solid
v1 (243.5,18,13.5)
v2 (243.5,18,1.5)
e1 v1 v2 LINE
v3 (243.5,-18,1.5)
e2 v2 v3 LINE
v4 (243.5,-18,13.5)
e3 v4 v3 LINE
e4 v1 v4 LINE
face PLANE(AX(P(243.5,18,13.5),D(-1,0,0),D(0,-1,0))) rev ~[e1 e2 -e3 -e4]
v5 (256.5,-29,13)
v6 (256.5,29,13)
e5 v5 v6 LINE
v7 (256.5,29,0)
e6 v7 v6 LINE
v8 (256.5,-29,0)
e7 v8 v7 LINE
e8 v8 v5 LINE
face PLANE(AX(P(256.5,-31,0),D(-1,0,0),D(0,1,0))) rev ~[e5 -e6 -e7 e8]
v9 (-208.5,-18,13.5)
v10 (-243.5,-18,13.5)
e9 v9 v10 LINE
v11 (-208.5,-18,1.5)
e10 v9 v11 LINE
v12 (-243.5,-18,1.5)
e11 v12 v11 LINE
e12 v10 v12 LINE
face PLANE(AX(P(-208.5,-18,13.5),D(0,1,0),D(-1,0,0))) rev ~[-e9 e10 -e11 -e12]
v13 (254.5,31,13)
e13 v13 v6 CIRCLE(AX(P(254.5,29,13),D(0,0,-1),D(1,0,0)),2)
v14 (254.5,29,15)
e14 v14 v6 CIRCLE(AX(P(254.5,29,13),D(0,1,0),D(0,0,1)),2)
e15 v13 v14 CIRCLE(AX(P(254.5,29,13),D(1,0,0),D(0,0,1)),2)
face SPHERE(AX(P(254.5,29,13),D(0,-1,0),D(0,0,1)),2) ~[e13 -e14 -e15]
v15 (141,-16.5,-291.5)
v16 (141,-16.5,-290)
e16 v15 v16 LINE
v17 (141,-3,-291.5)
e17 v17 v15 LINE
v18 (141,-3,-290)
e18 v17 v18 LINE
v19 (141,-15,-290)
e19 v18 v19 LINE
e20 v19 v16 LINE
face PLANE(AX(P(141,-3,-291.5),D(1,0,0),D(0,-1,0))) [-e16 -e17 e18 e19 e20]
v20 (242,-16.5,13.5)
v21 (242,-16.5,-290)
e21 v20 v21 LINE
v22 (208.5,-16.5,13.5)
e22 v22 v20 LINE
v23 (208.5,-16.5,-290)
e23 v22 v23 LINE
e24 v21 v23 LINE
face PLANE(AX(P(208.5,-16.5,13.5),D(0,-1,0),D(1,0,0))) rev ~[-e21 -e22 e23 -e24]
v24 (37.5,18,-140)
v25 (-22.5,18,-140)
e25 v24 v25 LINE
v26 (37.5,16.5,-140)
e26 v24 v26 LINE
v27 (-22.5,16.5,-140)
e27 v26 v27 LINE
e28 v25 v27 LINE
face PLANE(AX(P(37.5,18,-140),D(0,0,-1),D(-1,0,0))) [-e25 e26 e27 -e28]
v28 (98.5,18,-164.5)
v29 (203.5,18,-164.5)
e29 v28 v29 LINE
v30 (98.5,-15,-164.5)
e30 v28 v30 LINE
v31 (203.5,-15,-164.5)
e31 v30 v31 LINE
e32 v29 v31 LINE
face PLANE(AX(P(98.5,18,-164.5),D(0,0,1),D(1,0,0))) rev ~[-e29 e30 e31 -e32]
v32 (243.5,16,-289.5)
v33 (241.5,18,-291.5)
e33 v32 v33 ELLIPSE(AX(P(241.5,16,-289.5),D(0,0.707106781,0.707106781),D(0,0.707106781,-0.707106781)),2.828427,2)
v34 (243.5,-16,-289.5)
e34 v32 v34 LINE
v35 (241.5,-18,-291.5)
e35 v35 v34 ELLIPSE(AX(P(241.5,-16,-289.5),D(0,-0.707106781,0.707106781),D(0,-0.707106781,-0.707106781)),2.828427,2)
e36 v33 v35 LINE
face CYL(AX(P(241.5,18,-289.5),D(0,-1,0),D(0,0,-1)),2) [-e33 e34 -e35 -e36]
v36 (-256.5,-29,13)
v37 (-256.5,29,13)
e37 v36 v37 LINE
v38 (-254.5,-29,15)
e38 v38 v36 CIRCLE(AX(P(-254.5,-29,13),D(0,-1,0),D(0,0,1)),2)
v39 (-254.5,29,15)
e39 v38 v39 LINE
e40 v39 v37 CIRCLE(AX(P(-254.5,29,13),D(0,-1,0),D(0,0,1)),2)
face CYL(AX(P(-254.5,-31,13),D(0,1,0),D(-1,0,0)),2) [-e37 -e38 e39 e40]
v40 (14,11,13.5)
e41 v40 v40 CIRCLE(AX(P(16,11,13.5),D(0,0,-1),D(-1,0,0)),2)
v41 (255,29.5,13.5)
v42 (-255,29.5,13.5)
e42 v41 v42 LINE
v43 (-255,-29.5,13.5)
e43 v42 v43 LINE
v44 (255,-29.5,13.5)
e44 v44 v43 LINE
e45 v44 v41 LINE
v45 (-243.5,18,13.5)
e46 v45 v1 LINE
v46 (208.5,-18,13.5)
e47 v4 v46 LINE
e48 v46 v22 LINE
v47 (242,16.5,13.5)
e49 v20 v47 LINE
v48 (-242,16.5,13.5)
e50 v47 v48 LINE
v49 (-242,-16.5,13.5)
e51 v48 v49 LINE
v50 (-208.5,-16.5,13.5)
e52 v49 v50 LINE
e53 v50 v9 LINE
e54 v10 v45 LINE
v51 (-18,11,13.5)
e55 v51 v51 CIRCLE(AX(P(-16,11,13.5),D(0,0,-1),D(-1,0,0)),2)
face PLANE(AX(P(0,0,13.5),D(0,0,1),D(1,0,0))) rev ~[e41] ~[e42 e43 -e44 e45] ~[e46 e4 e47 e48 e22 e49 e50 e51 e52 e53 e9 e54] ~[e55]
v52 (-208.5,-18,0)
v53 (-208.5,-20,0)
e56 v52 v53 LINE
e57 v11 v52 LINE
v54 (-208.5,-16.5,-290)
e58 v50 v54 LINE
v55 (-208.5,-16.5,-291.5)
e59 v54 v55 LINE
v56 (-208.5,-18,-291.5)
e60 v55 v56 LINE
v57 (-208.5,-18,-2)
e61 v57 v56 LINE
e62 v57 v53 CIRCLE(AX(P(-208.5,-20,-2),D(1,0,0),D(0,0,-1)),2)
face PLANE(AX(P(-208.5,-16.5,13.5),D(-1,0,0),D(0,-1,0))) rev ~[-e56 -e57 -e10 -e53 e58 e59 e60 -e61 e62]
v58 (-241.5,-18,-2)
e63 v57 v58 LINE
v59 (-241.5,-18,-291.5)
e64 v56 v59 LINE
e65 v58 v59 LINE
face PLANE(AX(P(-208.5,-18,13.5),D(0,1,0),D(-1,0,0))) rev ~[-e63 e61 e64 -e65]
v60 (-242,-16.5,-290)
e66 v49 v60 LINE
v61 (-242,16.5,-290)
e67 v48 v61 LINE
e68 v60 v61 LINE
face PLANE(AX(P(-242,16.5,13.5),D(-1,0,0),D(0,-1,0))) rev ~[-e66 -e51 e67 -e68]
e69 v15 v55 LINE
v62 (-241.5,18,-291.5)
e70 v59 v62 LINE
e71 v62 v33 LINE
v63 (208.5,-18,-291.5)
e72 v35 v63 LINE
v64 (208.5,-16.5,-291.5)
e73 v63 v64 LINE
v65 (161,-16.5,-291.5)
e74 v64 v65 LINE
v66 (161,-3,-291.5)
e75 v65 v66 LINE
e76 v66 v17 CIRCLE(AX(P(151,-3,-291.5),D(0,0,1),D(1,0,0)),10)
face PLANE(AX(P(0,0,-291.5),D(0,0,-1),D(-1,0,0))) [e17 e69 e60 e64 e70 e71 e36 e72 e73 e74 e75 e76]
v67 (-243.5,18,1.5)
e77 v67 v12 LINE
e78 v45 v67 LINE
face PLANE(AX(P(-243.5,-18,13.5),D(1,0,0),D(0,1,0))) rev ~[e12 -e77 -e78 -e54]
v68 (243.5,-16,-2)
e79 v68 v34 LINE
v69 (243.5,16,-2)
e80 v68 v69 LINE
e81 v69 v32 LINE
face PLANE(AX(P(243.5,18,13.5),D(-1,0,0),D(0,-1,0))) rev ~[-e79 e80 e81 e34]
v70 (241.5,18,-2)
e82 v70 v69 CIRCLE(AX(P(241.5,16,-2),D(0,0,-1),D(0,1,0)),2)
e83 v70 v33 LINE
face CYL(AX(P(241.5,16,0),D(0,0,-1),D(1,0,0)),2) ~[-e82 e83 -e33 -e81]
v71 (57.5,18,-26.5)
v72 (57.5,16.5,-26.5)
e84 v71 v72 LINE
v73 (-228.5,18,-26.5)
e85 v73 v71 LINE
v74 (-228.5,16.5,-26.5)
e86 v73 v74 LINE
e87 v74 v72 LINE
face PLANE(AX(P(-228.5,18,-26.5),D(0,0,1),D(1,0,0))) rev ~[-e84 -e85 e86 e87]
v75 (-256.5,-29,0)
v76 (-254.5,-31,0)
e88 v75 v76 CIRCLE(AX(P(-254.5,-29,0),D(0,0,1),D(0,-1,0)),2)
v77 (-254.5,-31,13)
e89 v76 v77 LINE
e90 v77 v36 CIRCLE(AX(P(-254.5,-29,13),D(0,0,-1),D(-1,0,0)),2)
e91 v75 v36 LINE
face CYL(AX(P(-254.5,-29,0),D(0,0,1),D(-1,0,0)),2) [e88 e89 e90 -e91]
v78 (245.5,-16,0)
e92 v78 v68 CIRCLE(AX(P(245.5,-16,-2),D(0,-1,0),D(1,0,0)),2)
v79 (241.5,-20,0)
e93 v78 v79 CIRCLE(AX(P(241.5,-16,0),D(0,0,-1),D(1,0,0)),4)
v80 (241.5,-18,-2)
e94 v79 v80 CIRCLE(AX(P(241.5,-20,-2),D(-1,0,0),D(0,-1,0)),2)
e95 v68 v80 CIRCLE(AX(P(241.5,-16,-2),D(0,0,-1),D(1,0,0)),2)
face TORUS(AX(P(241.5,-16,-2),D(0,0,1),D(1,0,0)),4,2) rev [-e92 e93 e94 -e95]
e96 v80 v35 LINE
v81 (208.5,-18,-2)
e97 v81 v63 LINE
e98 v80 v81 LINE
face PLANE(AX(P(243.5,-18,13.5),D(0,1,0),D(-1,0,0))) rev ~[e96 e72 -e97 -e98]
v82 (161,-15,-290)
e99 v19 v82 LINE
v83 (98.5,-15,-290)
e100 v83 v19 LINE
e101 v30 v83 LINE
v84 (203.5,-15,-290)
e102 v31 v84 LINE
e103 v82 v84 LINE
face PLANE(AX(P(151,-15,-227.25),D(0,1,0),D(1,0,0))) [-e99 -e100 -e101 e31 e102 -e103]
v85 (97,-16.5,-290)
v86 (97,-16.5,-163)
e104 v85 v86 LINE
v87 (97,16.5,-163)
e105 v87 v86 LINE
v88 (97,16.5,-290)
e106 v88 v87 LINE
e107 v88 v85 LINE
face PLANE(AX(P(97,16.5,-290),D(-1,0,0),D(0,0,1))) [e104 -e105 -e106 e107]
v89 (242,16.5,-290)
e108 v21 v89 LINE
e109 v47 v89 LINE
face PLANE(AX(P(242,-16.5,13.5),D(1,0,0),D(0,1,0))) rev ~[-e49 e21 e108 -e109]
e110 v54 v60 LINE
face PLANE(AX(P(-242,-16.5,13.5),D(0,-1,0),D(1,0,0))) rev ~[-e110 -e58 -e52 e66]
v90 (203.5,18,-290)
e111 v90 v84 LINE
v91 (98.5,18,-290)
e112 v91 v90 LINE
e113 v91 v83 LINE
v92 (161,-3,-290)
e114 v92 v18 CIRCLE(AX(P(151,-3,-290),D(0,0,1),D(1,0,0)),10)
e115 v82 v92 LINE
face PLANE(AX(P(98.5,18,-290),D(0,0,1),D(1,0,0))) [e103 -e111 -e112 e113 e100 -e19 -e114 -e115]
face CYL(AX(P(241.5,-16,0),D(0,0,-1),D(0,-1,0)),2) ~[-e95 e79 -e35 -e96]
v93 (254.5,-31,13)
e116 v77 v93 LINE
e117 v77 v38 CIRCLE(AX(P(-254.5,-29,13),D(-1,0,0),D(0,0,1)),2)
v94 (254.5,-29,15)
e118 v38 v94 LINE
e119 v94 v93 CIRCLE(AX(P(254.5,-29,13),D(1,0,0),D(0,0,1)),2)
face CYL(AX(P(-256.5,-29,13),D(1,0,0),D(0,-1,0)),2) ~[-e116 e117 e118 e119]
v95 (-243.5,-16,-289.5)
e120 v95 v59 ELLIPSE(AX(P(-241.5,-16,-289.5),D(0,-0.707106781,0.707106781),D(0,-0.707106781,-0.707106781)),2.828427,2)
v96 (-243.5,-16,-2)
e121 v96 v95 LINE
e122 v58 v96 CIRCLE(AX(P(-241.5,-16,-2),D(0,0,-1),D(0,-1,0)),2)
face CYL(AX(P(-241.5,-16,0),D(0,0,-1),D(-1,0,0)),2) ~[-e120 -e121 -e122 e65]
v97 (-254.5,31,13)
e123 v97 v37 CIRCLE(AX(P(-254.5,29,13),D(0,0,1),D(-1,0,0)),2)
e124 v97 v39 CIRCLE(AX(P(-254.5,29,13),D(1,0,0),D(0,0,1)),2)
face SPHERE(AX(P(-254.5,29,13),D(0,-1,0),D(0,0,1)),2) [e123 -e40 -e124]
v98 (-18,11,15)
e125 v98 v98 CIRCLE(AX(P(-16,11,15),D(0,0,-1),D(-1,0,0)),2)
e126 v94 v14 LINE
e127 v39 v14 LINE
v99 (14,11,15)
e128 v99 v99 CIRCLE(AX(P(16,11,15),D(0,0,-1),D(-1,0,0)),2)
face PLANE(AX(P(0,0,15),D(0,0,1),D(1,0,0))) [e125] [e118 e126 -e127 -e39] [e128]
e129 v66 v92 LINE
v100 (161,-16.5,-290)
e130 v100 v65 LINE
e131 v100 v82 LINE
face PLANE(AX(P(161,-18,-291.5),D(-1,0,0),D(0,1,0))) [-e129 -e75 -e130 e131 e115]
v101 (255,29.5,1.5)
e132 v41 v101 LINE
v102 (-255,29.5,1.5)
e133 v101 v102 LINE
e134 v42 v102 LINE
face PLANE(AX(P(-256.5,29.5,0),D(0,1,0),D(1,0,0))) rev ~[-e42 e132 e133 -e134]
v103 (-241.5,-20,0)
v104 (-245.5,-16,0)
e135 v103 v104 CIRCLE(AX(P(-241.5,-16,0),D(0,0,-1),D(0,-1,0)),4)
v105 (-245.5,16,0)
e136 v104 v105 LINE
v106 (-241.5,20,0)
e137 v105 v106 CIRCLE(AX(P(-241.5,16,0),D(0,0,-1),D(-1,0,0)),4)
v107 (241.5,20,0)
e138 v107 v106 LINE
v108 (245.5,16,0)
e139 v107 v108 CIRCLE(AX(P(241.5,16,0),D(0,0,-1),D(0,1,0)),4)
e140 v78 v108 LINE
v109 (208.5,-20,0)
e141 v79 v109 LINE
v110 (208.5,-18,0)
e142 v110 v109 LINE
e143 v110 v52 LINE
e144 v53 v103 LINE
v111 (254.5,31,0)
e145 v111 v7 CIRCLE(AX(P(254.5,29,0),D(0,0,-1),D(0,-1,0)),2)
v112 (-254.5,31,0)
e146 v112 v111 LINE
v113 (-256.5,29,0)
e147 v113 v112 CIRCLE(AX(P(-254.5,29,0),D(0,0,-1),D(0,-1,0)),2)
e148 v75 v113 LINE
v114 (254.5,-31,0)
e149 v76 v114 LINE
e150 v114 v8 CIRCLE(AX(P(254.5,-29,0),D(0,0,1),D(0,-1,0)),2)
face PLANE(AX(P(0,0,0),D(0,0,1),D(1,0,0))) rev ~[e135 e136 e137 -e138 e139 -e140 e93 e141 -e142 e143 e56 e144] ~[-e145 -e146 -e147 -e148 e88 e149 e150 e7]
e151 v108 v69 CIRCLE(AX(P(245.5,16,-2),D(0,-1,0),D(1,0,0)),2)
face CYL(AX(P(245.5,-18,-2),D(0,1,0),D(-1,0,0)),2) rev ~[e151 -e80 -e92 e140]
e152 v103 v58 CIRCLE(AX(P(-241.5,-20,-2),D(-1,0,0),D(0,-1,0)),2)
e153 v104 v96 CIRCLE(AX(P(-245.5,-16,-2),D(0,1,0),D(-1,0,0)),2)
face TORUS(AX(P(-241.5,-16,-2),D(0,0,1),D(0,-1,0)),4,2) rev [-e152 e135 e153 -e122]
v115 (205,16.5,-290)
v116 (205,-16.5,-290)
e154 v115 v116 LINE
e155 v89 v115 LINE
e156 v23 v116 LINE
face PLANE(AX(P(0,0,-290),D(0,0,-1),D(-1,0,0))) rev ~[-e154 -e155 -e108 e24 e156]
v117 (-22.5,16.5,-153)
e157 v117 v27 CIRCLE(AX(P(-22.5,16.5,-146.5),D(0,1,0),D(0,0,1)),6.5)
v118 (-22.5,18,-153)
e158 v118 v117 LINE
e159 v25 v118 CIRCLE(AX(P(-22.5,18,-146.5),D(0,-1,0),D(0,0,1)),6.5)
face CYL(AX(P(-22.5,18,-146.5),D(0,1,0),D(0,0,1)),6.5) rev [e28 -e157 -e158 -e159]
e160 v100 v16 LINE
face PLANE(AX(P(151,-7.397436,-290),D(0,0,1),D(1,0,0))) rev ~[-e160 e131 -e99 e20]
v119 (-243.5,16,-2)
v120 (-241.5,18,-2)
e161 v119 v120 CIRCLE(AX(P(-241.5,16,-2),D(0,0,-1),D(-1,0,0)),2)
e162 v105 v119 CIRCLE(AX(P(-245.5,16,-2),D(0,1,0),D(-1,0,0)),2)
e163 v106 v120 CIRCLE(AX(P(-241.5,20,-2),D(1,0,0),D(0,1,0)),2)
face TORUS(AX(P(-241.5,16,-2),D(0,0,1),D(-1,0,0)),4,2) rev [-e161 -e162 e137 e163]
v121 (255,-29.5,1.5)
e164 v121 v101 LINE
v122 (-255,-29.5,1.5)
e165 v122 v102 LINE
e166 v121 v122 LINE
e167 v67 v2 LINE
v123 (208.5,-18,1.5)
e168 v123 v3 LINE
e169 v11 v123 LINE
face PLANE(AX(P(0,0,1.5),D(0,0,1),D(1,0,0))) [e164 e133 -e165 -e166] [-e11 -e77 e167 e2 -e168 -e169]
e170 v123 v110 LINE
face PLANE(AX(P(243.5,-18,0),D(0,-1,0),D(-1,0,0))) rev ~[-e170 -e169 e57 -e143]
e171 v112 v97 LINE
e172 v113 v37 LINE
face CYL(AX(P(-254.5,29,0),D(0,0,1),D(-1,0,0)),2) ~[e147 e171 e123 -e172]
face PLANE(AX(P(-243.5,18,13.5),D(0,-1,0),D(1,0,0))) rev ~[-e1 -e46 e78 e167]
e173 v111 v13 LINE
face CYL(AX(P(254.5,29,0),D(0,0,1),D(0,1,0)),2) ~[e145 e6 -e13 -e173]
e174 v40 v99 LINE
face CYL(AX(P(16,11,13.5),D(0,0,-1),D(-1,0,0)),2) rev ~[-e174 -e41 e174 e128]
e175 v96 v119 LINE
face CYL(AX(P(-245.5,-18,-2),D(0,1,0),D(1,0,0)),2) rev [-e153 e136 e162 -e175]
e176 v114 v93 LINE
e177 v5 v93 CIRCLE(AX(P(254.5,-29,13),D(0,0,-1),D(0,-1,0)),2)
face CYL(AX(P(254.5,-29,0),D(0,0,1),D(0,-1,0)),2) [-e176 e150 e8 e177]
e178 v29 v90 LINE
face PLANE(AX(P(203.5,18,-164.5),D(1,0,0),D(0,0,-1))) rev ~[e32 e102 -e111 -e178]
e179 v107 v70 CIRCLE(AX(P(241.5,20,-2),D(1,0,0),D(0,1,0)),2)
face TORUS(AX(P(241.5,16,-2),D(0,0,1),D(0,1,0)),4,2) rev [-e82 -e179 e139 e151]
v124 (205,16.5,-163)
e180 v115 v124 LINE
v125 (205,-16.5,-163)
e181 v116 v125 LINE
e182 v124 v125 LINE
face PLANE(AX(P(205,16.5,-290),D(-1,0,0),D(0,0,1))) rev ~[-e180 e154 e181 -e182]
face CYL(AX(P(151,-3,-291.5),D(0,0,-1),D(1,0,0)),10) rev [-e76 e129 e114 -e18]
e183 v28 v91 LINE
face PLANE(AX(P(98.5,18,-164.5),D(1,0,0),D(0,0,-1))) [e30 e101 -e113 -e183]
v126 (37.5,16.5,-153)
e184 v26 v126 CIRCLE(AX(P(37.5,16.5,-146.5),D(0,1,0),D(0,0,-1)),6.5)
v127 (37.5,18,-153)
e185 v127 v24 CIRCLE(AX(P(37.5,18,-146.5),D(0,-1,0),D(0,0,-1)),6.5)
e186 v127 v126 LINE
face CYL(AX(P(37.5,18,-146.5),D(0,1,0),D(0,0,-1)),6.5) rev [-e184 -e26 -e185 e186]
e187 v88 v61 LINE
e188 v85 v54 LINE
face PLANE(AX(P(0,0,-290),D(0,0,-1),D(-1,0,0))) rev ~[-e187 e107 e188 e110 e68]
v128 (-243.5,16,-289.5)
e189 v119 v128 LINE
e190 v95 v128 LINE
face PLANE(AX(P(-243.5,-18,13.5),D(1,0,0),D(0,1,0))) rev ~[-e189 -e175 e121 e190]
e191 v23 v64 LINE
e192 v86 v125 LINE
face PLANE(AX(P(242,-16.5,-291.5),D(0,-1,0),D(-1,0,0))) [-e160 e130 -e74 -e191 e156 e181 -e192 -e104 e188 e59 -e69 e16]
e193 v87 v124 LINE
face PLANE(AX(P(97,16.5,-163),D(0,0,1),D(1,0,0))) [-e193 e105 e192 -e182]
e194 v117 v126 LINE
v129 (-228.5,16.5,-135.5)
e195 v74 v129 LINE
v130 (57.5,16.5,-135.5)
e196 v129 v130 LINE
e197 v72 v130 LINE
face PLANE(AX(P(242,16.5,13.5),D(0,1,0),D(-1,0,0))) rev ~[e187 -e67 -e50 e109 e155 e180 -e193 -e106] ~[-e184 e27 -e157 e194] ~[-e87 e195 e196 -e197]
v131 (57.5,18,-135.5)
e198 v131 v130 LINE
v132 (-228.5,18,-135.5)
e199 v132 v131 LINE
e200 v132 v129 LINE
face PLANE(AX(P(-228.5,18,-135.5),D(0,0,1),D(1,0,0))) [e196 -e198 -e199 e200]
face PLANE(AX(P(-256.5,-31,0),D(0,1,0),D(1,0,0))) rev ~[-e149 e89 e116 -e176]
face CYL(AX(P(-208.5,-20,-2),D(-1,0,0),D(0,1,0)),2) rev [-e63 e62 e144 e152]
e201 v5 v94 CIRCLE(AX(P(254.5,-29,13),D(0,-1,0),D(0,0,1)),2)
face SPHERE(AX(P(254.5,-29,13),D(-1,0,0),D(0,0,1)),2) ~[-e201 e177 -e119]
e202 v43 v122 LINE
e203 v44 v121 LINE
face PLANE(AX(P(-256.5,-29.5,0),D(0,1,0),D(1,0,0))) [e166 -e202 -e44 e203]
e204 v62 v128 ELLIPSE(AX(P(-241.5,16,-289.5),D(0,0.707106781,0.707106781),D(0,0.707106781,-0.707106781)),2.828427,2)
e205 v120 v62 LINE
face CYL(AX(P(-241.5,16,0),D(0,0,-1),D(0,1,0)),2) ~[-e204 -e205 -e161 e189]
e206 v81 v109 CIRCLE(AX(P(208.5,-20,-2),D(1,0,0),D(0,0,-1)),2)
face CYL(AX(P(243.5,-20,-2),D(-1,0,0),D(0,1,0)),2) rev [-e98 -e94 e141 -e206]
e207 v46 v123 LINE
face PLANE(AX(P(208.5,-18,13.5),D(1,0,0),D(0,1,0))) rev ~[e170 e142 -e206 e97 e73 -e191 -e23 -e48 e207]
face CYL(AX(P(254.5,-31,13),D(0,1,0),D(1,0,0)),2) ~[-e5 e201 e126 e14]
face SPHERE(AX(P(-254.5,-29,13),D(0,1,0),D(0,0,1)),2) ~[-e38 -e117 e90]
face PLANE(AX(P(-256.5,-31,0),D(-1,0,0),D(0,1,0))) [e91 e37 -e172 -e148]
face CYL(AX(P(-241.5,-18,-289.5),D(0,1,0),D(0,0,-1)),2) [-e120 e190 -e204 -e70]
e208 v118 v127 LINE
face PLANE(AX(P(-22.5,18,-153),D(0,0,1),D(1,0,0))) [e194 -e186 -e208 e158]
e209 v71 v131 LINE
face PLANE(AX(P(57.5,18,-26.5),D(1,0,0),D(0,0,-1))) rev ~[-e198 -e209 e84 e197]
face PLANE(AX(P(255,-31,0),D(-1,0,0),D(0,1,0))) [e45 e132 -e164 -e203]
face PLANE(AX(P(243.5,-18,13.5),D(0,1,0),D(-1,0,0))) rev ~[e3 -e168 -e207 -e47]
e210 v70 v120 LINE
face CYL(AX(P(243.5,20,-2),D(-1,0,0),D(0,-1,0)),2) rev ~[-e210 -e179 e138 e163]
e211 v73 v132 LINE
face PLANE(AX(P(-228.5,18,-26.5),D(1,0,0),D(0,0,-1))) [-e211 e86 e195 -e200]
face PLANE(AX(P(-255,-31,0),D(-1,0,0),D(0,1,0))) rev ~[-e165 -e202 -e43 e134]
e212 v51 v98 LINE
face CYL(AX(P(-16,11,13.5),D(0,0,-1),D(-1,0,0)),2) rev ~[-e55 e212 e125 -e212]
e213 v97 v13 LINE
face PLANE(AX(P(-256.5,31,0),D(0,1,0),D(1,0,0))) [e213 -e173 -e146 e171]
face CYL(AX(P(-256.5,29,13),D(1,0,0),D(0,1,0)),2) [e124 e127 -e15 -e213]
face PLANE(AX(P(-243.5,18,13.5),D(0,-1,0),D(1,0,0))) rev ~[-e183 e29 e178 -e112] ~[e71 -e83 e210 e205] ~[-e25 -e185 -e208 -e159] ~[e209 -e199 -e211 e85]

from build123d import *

# Parameters (mm, degrees)
SKETCH_1_W          = 513
SKETCH_1_H          = 62
EXTRUDE_1_DEPTH     = 15
SHELL_1_T           = 1.5
SKETCH_2_W          = 487
SKETCH_2_H          = 36
CUT_EXTRUDE_1_DEPTH = 2
EXTRUDE_2_DEPTH     = 305
SKETCH_4_W          = 484
SKETCH_4_H          = 33
EXTRUDE_3_DEPTH     = 1.5
SKETCH_6_W          = 108
SKETCH_6_H          = 127
EXTRUDE_4_DEPTH     = 33
SKETCH_7_W          = 105
SKETCH_7_H          = 125.5
CUT_EXTRUDE_2_DEPTH = 33
CUT_EXTRUDE_3_DEPTH = 1.5
SKETCH_9_W          = 286
SKETCH_9_H          = 109
CUT_EXTRUDE_4_DEPTH = 1.5
CUT_EXTRUDE_5_DEPTH = 10
SKETCH_11_R         = 2
CUT_EXTRUDE_6_DEPTH = 400.722716392
FILLET_1_R          = 2


with BuildPart() as part:
    # 草图1 → 凸台-拉伸1 (new body)
    with BuildSketch(Plane.XY):
        Rectangle(SKETCH_1_W, SKETCH_1_H)
    extrude(amount=EXTRUDE_1_DEPTH)

    # 抽壳1 (no face opened: a closed hollow body)
    add(offset(amount=-SHELL_1_T, mode=Mode.PRIVATE), mode=Mode.SUBTRACT)

    # 草图2 → 切除-拉伸1 (cut)
    with BuildSketch(Plane(origin=(0, 0, 0), x_dir=(-1, 0, 0), z_dir=(0, 0, -1))):
        Rectangle(SKETCH_2_W, SKETCH_2_H)
    extrude(amount=-CUT_EXTRUDE_1_DEPTH, mode=Mode.SUBTRACT)

    # 草图3 → 凸台-拉伸2 (add)
    with BuildSketch(Plane(origin=(0, 0, 13.5), x_dir=(-1, 0, 0), z_dir=(0, 0, -1))):
        Polygon((243.5, 18), (-243.5, 18), (-243.5, -18), (-208.5, -18), (-208.5, -16.5), (-242, -16.5), (-242, 16.5), (242, 16.5), (242, -16.5), (208.5, -16.5), (208.5, -18), (243.5, -18), align=None)
    extrude(amount=EXTRUDE_2_DEPTH)

    # 草图4 → 凸台-拉伸3 (add)
    with BuildSketch(Plane(origin=(0, 0, -291.5), x_dir=(-1, 0, 0), z_dir=(0, 0, -1))):
        Rectangle(SKETCH_4_W, SKETCH_4_H)
    extrude(amount=-EXTRUDE_3_DEPTH)

    # 草图6 → 凸台-拉伸4 (add)
    with BuildSketch(Plane.XZ.offset(-16.5)):
        with Locations((151, -226.5)):
            Rectangle(SKETCH_6_W, SKETCH_6_H)
    extrude(amount=EXTRUDE_4_DEPTH)

    # 草图7 → 切除-拉伸2 (cut)
    with BuildSketch(Plane(origin=(0, 18, 0), x_dir=(1, 0, 0), z_dir=(0, 1, 0))):
        with Locations((151, 227.25)):
            Rectangle(SKETCH_7_W, SKETCH_7_H)
    extrude(amount=-CUT_EXTRUDE_2_DEPTH, mode=Mode.SUBTRACT)

    # 草图8 → 切除-拉伸3 (cut)
    with BuildSketch(Plane(origin=(0, 0, -291.5), x_dir=(-1, 0, 0), z_dir=(0, 0, -1))):
        with BuildLine():
            Line((-161, -18), (-161, -3))
            ThreePointArc((-161, -3), (-151, 7), (-141, -3))
            Line((-141, -3), (-141, -18))
            Line((-141, -18), (-161, -18))
        make_face()
    extrude(amount=-CUT_EXTRUDE_3_DEPTH, mode=Mode.SUBTRACT)

    # 草图9 → 切除-拉伸4 (cut)
    with BuildSketch(Plane(origin=(0, 18, 0), x_dir=(1, 0, 0), z_dir=(0, 1, 0))):
        with Locations((-85.5, 81)):
            Rectangle(SKETCH_9_W, SKETCH_9_H)
    extrude(amount=-CUT_EXTRUDE_4_DEPTH, mode=Mode.SUBTRACT)

    # 草图10 → 切除-拉伸5 (cut)
    with BuildSketch(Plane(origin=(0, 18, 0), x_dir=(1, 0, 0), z_dir=(0, 1, 0))):
        with BuildLine():
            Line((-22.5, 153), (37.5, 153))
            ThreePointArc((37.5, 153), (44, 146.5), (37.5, 140))
            Line((37.5, 140), (-22.5, 140))
            ThreePointArc((-22.5, 140), (-29, 146.5), (-22.5, 153))
        make_face()
    extrude(amount=-CUT_EXTRUDE_5_DEPTH, mode=Mode.SUBTRACT)

    # 草图11 → 切除-拉伸6 (cut, through all)
    with BuildSketch(Plane(origin=(0, 0, 13.5), x_dir=(-1, 0, 0), z_dir=(0, 0, -1))):
        with Locations((-16, 11)):
            Circle(SKETCH_11_R)
        with Locations((16, 11)):
            Circle(SKETCH_11_R)
    extrude(amount=-CUT_EXTRUDE_6_DEPTH, mode=Mode.SUBTRACT)

    # 圆角1
    fillet_1_edges = [part.edges().sort_by_distance(p)[0] for p in [
        (-256.5, 0, 15),
        (0, -31, 15),
        (-243.5, 0, 0),
        (0, 18, 0),
        (243.5, 0, 0),
        (226, -18, 0),
        (256.5, 0, 15),
        (-243.5, -18, -145.75),
        (-243.5, 18, -145.75),
        (243.5, 18, -145.75),
        (243.5, -18, -145.75),
        (-226, -18, 0),
        (-243.5, 0, -291.5),
        (243.5, 0, -291.5),
        (0, 31, 15),
        (256.5, -31, 7.5),
        (-256.5, -31, 7.5),
        (-256.5, 31, 7.5),
        (256.5, 31, 7.5),
    ]]
    fillet(fillet_1_edges, radius=FILLET_1_R)


solid = part.part
